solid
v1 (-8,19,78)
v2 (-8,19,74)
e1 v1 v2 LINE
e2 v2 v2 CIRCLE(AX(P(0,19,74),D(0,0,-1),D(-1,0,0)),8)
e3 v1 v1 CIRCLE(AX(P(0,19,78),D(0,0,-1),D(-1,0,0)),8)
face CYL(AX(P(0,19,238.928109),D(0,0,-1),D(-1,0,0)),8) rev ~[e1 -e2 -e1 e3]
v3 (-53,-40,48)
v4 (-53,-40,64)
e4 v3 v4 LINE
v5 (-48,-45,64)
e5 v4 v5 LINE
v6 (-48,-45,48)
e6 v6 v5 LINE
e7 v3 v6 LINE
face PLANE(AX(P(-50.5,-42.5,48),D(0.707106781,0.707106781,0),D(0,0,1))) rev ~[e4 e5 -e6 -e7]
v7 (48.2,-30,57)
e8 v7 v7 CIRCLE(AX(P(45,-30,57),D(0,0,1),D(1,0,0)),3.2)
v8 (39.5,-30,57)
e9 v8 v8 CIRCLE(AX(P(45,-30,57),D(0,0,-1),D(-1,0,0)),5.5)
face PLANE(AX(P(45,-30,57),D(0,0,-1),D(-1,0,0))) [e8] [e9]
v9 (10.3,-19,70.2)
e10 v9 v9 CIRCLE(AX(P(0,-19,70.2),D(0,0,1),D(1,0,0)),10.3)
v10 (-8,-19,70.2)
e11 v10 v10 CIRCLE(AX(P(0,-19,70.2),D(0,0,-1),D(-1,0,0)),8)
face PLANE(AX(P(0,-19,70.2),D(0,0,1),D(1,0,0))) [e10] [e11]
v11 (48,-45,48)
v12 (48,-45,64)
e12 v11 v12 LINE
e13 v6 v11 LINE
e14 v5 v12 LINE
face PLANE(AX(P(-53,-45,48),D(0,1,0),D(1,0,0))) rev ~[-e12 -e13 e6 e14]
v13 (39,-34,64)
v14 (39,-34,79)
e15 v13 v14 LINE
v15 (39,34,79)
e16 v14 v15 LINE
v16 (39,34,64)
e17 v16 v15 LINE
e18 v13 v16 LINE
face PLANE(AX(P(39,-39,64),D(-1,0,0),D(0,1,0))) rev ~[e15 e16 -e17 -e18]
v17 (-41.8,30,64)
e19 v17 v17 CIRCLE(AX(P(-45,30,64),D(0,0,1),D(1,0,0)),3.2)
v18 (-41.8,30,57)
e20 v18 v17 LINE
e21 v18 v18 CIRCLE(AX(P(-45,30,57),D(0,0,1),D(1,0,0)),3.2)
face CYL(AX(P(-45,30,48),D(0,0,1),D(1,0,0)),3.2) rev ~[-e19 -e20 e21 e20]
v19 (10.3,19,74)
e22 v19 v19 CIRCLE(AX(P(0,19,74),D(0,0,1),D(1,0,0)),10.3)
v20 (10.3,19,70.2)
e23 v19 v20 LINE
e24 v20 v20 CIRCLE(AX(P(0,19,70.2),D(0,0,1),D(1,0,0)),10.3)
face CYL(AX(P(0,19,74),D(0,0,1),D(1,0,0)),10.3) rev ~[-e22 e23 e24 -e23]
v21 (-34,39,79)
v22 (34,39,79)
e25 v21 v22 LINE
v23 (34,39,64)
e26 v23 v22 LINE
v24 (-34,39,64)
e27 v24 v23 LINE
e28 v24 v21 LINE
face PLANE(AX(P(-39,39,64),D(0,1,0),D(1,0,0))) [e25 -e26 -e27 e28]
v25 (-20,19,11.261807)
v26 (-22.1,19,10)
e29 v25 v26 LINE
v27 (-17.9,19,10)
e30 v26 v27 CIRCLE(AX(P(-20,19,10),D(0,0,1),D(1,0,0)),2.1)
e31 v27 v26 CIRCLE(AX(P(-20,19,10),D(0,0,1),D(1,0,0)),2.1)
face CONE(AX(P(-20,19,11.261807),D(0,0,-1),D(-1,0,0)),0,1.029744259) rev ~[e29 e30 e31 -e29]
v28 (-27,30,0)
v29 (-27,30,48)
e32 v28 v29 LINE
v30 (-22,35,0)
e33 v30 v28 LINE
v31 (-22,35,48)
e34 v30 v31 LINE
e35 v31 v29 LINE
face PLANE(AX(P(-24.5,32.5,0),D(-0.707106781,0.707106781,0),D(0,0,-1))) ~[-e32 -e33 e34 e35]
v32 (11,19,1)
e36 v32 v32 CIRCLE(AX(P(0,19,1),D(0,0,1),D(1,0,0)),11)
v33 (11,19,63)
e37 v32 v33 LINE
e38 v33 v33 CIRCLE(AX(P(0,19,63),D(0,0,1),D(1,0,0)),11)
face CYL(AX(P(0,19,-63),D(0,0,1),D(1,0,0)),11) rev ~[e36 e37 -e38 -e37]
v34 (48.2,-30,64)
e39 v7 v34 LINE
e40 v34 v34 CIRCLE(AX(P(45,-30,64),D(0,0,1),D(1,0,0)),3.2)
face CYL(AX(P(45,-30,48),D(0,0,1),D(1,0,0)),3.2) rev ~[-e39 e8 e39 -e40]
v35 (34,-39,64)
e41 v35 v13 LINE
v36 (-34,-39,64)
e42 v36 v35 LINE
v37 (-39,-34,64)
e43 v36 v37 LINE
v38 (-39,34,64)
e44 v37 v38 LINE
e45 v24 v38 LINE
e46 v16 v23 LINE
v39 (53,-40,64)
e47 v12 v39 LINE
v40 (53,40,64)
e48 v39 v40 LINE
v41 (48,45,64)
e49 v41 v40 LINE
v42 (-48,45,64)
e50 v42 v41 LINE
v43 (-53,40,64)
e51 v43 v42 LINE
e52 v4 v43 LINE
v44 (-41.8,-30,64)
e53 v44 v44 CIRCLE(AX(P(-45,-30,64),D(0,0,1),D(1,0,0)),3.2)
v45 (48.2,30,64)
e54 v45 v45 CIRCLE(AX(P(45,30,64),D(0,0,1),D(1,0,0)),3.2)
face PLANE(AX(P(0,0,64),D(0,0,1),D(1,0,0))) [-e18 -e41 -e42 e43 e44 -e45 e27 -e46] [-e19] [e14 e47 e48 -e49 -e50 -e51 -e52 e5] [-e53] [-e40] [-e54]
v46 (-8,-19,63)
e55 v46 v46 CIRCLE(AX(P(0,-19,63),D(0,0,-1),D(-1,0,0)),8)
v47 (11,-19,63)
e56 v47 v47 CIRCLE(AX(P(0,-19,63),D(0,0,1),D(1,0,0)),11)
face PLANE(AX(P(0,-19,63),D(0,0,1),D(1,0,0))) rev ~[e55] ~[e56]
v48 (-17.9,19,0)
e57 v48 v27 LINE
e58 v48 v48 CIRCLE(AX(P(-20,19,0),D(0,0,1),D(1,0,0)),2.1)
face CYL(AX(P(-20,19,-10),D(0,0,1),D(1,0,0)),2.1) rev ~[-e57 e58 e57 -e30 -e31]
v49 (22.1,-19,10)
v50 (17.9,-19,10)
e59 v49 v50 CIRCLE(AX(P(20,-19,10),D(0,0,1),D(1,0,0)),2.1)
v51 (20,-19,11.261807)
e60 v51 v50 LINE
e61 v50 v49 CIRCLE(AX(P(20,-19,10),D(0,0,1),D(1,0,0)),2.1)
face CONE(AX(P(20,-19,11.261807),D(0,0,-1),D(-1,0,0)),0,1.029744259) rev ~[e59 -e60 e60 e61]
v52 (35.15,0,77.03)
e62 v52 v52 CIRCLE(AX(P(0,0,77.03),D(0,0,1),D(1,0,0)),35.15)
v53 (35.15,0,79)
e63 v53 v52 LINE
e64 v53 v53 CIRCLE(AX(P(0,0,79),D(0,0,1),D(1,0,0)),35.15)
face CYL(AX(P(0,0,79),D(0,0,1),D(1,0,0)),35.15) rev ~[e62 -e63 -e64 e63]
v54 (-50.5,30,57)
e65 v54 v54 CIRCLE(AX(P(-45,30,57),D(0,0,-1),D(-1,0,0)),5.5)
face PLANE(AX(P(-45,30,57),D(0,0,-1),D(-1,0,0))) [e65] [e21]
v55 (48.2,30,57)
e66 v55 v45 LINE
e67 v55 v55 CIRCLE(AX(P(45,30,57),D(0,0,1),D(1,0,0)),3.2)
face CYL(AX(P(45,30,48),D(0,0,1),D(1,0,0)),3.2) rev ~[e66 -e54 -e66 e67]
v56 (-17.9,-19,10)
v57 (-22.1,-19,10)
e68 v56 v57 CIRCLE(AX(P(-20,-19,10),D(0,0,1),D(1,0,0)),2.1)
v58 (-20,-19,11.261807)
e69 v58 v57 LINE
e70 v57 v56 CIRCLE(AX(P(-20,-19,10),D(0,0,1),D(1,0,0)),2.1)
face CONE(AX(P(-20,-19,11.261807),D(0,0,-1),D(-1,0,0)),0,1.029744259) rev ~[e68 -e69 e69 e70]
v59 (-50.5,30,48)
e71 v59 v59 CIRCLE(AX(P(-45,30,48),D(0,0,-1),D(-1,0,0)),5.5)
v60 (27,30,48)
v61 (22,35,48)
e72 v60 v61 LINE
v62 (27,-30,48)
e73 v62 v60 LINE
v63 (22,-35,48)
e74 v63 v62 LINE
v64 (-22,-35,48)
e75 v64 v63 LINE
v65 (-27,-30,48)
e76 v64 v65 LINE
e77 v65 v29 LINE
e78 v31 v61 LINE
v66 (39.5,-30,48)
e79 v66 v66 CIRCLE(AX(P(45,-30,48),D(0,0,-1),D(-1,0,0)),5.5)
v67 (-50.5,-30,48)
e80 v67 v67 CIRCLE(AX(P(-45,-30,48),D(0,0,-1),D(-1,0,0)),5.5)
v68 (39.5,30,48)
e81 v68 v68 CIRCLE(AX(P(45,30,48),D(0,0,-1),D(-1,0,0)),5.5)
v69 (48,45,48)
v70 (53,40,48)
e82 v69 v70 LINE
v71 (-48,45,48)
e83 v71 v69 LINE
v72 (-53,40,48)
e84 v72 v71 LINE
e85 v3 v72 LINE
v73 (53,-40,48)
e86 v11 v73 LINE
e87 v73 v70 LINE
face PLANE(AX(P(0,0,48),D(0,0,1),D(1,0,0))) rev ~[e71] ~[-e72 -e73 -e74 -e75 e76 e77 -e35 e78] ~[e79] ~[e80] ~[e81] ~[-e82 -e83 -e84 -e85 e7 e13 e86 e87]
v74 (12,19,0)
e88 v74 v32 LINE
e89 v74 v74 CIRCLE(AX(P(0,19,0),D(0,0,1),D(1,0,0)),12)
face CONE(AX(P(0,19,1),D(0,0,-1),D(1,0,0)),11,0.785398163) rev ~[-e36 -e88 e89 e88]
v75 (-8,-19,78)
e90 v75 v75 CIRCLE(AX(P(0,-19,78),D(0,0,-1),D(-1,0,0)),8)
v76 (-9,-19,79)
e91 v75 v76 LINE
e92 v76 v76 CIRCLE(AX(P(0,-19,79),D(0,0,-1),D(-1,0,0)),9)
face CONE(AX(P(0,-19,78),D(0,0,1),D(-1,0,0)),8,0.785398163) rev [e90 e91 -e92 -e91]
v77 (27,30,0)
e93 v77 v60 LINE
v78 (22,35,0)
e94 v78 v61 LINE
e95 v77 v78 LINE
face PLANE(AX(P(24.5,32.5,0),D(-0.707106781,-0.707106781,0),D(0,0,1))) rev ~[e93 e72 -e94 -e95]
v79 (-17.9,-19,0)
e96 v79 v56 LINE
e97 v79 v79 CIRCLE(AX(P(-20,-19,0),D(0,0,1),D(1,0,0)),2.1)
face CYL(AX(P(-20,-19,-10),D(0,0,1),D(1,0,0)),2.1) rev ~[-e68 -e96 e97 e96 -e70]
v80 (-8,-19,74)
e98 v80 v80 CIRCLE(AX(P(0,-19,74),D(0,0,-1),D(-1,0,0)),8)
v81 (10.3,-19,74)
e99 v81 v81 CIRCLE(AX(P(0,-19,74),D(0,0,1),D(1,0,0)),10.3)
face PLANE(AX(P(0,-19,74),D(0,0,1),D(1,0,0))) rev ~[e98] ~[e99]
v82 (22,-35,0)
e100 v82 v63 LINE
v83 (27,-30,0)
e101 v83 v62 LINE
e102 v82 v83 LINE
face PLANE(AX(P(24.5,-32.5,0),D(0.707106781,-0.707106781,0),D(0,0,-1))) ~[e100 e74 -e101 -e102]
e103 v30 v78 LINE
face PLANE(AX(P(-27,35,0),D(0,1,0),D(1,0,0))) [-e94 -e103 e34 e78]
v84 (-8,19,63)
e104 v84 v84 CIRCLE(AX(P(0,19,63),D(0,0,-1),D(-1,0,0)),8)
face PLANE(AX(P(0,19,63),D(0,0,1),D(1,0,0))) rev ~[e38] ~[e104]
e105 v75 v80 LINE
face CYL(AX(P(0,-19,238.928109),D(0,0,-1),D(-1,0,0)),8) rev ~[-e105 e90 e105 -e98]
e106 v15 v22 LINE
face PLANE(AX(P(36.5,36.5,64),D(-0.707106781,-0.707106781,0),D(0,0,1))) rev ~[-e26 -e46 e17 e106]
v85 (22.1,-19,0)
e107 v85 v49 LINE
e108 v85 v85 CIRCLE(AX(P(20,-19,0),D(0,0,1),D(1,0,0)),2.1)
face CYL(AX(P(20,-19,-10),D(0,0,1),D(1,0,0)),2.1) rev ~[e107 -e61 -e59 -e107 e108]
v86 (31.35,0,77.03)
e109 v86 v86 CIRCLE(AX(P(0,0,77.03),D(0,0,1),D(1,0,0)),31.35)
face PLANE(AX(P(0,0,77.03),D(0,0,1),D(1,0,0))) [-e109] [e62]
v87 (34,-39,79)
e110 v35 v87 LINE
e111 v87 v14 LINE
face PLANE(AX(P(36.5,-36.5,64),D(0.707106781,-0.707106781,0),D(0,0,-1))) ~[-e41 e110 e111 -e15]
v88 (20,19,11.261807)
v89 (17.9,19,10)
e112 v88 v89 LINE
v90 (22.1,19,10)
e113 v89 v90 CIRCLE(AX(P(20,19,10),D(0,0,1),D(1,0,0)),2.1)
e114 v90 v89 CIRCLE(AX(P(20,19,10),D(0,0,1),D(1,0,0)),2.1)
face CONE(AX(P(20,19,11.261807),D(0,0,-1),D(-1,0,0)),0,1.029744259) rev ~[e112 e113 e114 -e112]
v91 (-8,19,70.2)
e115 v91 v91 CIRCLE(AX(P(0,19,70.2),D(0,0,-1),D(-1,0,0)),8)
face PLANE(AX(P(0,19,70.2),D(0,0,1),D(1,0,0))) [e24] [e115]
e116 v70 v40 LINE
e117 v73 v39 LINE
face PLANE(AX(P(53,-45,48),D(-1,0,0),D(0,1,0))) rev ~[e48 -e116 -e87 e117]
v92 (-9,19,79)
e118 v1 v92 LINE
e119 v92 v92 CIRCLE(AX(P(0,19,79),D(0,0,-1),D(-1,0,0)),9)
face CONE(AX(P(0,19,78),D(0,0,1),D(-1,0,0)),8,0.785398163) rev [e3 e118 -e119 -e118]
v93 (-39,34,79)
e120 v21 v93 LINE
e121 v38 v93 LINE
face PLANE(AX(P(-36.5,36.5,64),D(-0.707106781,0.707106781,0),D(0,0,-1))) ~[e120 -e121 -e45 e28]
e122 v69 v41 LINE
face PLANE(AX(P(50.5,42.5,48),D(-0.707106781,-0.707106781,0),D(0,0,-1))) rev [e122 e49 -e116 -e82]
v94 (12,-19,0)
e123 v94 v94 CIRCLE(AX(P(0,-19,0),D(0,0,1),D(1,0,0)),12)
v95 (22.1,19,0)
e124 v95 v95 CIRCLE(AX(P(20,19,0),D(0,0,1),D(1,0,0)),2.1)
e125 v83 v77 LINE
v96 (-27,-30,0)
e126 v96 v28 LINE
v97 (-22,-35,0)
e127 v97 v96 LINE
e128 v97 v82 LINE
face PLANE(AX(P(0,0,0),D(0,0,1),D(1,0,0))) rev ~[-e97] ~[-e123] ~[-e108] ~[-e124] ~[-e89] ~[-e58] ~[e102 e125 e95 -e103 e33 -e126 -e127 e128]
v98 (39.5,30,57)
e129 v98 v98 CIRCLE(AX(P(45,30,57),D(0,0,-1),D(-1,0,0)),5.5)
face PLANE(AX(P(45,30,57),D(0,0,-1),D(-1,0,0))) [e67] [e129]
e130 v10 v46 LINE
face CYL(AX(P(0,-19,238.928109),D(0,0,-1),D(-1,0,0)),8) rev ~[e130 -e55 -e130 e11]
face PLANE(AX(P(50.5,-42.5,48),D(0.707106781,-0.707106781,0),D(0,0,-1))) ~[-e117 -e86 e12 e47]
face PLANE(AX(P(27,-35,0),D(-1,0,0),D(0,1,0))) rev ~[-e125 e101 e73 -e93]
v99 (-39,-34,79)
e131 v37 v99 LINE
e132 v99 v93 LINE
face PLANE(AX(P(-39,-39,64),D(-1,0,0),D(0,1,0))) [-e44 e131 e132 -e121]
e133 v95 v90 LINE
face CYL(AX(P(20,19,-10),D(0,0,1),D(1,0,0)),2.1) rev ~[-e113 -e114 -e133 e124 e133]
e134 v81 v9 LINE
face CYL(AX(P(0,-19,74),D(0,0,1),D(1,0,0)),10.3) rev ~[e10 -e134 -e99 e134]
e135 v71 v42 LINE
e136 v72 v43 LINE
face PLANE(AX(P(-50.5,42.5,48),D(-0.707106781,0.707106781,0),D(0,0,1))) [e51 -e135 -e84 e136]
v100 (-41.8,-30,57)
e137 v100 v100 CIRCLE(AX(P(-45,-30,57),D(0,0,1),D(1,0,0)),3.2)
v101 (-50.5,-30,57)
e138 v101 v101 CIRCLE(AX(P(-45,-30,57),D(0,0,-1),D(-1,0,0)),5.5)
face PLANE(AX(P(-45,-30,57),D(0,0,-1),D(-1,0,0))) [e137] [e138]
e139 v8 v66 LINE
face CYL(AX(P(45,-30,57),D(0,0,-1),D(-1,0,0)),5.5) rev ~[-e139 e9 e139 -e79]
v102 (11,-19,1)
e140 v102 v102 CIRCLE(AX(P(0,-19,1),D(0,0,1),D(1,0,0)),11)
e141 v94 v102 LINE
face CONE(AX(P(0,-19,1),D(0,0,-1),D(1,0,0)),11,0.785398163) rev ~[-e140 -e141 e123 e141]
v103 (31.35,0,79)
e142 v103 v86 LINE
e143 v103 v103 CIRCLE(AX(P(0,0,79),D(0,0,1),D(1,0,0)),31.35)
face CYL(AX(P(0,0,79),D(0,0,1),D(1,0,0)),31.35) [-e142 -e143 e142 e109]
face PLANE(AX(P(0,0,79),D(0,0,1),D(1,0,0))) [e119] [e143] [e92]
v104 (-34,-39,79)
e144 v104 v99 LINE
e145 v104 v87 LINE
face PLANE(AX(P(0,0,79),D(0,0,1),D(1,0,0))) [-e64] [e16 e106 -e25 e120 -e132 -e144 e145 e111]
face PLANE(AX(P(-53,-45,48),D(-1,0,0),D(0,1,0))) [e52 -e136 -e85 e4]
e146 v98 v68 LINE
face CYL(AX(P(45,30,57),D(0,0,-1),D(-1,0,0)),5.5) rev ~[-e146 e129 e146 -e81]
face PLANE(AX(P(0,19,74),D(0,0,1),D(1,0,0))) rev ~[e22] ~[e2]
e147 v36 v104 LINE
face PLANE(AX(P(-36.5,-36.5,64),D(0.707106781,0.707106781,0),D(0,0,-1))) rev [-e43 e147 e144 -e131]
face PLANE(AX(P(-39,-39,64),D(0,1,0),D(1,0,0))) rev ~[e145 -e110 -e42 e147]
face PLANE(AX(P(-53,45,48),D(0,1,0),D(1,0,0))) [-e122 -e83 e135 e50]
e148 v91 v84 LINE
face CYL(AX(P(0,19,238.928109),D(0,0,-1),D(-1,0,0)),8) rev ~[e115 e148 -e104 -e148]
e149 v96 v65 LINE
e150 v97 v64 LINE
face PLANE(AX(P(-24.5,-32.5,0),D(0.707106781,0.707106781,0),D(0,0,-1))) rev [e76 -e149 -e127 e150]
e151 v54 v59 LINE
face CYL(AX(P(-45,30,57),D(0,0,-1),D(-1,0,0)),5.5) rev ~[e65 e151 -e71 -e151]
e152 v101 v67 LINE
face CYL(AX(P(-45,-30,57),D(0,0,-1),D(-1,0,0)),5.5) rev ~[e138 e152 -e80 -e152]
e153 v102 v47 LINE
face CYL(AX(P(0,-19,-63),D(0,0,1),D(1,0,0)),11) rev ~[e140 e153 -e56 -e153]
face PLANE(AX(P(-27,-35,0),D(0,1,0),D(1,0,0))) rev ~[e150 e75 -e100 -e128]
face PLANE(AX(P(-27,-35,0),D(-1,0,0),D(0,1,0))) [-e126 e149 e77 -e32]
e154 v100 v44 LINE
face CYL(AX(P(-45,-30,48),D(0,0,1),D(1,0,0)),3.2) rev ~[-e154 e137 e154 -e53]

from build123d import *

# Parameters (mm, degrees)
SKETCH1_W             = 54
SKETCH1_H             = 70
BOSS_EXTRUDE1_DEPTH   = 48
SKETCH2_W             = 106
SKETCH2_H             = 90
BOSS_EXTRUDE2_DEPTH   = 16
SKETCH3_W             = 78
SKETCH3_H             = 78
BOSS_EXTRUDE3_DEPTH   = 15
CHAMFER1_SIZE         = 5
SKETCH4_R             = 35.15
SKETCH4_R_2           = 31.35
CUT_EXTRUDE1_DEPTH    = 1.97
HOLE1_D               = 16
HOLE2_D               = 22
HOLE2_DEPTH           = 63
CHAMFER2_SIZE         = 1
M5_TAPPED_HOLE1_D     = 4.2
M5_TAPPED_HOLE1_DEPTH = 10
M5_TAPPED_HOLE1_TIP   = 1.2618073
HOLE3_D               = 6.4
HOLE3_CBORE_D         = 11
HOLE3_CBORE_DEPTH     = 9
SKETCH16_R            = 10.3
CUT_EXTRUDE2_DEPTH    = 3.8


with BuildPart() as part:
    # Sketch1 → Boss-Extrude1 (new body)
    with BuildSketch(Plane.XY):
        Rectangle(SKETCH1_W, SKETCH1_H)
    extrude(amount=BOSS_EXTRUDE1_DEPTH)

    # Sketch2 → Boss-Extrude2 (add)
    with BuildSketch(Plane.XY.offset(48)):
        Rectangle(SKETCH2_W, SKETCH2_H)
    extrude(amount=BOSS_EXTRUDE2_DEPTH)

    # Sketch3 → Boss-Extrude3 (add)
    with BuildSketch(Plane.XY.offset(64)):
        Rectangle(SKETCH3_W, SKETCH3_H)
    extrude(amount=BOSS_EXTRUDE3_DEPTH)

    # Chamfer1
    chamfer1_edges = [part.edges().sort_by_distance(p)[0] for p in [
        (-53, 45, 56),
        (-53, -45, 56),
        (53, -45, 56),
        (53, 45, 56),
        (-39, 39, 71.5),
        (-39, -39, 71.5),
        (39, -39, 71.5),
        (39, 39, 71.5),
        (27, -35, 24),
        (-27, -35, 24),
        (-27, 35, 24),
        (27, 35, 24),
    ]]
    chamfer(chamfer1_edges, length=CHAMFER1_SIZE)

    # Sketch4 → Cut-Extrude1 (cut)
    with BuildSketch(Plane.XY.offset(79)):
        Circle(SKETCH4_R)
        Circle(SKETCH4_R_2, mode=Mode.SUBTRACT)
    extrude(amount=-CUT_EXTRUDE1_DEPTH, mode=Mode.SUBTRACT)

    # Hole1 (through all)
    with Locations(Plane.XY.offset(79)):
        with Locations((0, -19), (0, 19)):
            Hole(HOLE1_D / 2)

    # Hole2
    with Locations(Plane(origin=(0, 0, 0), x_dir=(-1, 0, 0), z_dir=(0, 0, -1))):
        with Locations((0, 19), (0, -19)):
            Hole(HOLE2_D / 2, depth=HOLE2_DEPTH)

    # Chamfer2
    chamfer2_edges = [part.edges().sort_by_distance(p)[0] for p in [
        (8, 19, 79),
        (8, -19, 79),
        (-11, -19, 0),
        (-11, 19, 0),
    ]]
    chamfer(chamfer2_edges, length=CHAMFER2_SIZE)

    # M5 Tapped Hole1
    with Locations(Plane(origin=(0, 0, 0), x_dir=(-1, 0, 0), z_dir=(0, 0, -1))):
        with Locations((20, -19), (20, 19), (-20, 19), (-20, -19)):
            Hole(M5_TAPPED_HOLE1_D / 2, depth=M5_TAPPED_HOLE1_DEPTH)
            with Locations((0, 0, -(M5_TAPPED_HOLE1_DEPTH + M5_TAPPED_HOLE1_TIP / 2))):  # 118° drill point
                Cone(0, M5_TAPPED_HOLE1_D / 2, M5_TAPPED_HOLE1_TIP, mode=Mode.SUBTRACT)

    # Hole3 (through all)
    with Locations(Plane(origin=(0, 0, 48), x_dir=(-1, 0, 0), z_dir=(0, 0, -1))):
        with Locations((45, -30), (45, 30), (-45, 30), (-45, -30)):
            CounterBoreHole(HOLE3_D / 2, HOLE3_CBORE_D / 2, HOLE3_CBORE_DEPTH)

    # Sketch16 → Cut-Extrude2 (cut)
    with BuildSketch(Plane.XY.offset(74)):
        with Locations((0, 19)):
            Circle(SKETCH16_R)
        with Locations((0, -19)):
            Circle(SKETCH16_R)
    extrude(amount=-CUT_EXTRUDE2_DEPTH, mode=Mode.SUBTRACT)


solid = part.part
